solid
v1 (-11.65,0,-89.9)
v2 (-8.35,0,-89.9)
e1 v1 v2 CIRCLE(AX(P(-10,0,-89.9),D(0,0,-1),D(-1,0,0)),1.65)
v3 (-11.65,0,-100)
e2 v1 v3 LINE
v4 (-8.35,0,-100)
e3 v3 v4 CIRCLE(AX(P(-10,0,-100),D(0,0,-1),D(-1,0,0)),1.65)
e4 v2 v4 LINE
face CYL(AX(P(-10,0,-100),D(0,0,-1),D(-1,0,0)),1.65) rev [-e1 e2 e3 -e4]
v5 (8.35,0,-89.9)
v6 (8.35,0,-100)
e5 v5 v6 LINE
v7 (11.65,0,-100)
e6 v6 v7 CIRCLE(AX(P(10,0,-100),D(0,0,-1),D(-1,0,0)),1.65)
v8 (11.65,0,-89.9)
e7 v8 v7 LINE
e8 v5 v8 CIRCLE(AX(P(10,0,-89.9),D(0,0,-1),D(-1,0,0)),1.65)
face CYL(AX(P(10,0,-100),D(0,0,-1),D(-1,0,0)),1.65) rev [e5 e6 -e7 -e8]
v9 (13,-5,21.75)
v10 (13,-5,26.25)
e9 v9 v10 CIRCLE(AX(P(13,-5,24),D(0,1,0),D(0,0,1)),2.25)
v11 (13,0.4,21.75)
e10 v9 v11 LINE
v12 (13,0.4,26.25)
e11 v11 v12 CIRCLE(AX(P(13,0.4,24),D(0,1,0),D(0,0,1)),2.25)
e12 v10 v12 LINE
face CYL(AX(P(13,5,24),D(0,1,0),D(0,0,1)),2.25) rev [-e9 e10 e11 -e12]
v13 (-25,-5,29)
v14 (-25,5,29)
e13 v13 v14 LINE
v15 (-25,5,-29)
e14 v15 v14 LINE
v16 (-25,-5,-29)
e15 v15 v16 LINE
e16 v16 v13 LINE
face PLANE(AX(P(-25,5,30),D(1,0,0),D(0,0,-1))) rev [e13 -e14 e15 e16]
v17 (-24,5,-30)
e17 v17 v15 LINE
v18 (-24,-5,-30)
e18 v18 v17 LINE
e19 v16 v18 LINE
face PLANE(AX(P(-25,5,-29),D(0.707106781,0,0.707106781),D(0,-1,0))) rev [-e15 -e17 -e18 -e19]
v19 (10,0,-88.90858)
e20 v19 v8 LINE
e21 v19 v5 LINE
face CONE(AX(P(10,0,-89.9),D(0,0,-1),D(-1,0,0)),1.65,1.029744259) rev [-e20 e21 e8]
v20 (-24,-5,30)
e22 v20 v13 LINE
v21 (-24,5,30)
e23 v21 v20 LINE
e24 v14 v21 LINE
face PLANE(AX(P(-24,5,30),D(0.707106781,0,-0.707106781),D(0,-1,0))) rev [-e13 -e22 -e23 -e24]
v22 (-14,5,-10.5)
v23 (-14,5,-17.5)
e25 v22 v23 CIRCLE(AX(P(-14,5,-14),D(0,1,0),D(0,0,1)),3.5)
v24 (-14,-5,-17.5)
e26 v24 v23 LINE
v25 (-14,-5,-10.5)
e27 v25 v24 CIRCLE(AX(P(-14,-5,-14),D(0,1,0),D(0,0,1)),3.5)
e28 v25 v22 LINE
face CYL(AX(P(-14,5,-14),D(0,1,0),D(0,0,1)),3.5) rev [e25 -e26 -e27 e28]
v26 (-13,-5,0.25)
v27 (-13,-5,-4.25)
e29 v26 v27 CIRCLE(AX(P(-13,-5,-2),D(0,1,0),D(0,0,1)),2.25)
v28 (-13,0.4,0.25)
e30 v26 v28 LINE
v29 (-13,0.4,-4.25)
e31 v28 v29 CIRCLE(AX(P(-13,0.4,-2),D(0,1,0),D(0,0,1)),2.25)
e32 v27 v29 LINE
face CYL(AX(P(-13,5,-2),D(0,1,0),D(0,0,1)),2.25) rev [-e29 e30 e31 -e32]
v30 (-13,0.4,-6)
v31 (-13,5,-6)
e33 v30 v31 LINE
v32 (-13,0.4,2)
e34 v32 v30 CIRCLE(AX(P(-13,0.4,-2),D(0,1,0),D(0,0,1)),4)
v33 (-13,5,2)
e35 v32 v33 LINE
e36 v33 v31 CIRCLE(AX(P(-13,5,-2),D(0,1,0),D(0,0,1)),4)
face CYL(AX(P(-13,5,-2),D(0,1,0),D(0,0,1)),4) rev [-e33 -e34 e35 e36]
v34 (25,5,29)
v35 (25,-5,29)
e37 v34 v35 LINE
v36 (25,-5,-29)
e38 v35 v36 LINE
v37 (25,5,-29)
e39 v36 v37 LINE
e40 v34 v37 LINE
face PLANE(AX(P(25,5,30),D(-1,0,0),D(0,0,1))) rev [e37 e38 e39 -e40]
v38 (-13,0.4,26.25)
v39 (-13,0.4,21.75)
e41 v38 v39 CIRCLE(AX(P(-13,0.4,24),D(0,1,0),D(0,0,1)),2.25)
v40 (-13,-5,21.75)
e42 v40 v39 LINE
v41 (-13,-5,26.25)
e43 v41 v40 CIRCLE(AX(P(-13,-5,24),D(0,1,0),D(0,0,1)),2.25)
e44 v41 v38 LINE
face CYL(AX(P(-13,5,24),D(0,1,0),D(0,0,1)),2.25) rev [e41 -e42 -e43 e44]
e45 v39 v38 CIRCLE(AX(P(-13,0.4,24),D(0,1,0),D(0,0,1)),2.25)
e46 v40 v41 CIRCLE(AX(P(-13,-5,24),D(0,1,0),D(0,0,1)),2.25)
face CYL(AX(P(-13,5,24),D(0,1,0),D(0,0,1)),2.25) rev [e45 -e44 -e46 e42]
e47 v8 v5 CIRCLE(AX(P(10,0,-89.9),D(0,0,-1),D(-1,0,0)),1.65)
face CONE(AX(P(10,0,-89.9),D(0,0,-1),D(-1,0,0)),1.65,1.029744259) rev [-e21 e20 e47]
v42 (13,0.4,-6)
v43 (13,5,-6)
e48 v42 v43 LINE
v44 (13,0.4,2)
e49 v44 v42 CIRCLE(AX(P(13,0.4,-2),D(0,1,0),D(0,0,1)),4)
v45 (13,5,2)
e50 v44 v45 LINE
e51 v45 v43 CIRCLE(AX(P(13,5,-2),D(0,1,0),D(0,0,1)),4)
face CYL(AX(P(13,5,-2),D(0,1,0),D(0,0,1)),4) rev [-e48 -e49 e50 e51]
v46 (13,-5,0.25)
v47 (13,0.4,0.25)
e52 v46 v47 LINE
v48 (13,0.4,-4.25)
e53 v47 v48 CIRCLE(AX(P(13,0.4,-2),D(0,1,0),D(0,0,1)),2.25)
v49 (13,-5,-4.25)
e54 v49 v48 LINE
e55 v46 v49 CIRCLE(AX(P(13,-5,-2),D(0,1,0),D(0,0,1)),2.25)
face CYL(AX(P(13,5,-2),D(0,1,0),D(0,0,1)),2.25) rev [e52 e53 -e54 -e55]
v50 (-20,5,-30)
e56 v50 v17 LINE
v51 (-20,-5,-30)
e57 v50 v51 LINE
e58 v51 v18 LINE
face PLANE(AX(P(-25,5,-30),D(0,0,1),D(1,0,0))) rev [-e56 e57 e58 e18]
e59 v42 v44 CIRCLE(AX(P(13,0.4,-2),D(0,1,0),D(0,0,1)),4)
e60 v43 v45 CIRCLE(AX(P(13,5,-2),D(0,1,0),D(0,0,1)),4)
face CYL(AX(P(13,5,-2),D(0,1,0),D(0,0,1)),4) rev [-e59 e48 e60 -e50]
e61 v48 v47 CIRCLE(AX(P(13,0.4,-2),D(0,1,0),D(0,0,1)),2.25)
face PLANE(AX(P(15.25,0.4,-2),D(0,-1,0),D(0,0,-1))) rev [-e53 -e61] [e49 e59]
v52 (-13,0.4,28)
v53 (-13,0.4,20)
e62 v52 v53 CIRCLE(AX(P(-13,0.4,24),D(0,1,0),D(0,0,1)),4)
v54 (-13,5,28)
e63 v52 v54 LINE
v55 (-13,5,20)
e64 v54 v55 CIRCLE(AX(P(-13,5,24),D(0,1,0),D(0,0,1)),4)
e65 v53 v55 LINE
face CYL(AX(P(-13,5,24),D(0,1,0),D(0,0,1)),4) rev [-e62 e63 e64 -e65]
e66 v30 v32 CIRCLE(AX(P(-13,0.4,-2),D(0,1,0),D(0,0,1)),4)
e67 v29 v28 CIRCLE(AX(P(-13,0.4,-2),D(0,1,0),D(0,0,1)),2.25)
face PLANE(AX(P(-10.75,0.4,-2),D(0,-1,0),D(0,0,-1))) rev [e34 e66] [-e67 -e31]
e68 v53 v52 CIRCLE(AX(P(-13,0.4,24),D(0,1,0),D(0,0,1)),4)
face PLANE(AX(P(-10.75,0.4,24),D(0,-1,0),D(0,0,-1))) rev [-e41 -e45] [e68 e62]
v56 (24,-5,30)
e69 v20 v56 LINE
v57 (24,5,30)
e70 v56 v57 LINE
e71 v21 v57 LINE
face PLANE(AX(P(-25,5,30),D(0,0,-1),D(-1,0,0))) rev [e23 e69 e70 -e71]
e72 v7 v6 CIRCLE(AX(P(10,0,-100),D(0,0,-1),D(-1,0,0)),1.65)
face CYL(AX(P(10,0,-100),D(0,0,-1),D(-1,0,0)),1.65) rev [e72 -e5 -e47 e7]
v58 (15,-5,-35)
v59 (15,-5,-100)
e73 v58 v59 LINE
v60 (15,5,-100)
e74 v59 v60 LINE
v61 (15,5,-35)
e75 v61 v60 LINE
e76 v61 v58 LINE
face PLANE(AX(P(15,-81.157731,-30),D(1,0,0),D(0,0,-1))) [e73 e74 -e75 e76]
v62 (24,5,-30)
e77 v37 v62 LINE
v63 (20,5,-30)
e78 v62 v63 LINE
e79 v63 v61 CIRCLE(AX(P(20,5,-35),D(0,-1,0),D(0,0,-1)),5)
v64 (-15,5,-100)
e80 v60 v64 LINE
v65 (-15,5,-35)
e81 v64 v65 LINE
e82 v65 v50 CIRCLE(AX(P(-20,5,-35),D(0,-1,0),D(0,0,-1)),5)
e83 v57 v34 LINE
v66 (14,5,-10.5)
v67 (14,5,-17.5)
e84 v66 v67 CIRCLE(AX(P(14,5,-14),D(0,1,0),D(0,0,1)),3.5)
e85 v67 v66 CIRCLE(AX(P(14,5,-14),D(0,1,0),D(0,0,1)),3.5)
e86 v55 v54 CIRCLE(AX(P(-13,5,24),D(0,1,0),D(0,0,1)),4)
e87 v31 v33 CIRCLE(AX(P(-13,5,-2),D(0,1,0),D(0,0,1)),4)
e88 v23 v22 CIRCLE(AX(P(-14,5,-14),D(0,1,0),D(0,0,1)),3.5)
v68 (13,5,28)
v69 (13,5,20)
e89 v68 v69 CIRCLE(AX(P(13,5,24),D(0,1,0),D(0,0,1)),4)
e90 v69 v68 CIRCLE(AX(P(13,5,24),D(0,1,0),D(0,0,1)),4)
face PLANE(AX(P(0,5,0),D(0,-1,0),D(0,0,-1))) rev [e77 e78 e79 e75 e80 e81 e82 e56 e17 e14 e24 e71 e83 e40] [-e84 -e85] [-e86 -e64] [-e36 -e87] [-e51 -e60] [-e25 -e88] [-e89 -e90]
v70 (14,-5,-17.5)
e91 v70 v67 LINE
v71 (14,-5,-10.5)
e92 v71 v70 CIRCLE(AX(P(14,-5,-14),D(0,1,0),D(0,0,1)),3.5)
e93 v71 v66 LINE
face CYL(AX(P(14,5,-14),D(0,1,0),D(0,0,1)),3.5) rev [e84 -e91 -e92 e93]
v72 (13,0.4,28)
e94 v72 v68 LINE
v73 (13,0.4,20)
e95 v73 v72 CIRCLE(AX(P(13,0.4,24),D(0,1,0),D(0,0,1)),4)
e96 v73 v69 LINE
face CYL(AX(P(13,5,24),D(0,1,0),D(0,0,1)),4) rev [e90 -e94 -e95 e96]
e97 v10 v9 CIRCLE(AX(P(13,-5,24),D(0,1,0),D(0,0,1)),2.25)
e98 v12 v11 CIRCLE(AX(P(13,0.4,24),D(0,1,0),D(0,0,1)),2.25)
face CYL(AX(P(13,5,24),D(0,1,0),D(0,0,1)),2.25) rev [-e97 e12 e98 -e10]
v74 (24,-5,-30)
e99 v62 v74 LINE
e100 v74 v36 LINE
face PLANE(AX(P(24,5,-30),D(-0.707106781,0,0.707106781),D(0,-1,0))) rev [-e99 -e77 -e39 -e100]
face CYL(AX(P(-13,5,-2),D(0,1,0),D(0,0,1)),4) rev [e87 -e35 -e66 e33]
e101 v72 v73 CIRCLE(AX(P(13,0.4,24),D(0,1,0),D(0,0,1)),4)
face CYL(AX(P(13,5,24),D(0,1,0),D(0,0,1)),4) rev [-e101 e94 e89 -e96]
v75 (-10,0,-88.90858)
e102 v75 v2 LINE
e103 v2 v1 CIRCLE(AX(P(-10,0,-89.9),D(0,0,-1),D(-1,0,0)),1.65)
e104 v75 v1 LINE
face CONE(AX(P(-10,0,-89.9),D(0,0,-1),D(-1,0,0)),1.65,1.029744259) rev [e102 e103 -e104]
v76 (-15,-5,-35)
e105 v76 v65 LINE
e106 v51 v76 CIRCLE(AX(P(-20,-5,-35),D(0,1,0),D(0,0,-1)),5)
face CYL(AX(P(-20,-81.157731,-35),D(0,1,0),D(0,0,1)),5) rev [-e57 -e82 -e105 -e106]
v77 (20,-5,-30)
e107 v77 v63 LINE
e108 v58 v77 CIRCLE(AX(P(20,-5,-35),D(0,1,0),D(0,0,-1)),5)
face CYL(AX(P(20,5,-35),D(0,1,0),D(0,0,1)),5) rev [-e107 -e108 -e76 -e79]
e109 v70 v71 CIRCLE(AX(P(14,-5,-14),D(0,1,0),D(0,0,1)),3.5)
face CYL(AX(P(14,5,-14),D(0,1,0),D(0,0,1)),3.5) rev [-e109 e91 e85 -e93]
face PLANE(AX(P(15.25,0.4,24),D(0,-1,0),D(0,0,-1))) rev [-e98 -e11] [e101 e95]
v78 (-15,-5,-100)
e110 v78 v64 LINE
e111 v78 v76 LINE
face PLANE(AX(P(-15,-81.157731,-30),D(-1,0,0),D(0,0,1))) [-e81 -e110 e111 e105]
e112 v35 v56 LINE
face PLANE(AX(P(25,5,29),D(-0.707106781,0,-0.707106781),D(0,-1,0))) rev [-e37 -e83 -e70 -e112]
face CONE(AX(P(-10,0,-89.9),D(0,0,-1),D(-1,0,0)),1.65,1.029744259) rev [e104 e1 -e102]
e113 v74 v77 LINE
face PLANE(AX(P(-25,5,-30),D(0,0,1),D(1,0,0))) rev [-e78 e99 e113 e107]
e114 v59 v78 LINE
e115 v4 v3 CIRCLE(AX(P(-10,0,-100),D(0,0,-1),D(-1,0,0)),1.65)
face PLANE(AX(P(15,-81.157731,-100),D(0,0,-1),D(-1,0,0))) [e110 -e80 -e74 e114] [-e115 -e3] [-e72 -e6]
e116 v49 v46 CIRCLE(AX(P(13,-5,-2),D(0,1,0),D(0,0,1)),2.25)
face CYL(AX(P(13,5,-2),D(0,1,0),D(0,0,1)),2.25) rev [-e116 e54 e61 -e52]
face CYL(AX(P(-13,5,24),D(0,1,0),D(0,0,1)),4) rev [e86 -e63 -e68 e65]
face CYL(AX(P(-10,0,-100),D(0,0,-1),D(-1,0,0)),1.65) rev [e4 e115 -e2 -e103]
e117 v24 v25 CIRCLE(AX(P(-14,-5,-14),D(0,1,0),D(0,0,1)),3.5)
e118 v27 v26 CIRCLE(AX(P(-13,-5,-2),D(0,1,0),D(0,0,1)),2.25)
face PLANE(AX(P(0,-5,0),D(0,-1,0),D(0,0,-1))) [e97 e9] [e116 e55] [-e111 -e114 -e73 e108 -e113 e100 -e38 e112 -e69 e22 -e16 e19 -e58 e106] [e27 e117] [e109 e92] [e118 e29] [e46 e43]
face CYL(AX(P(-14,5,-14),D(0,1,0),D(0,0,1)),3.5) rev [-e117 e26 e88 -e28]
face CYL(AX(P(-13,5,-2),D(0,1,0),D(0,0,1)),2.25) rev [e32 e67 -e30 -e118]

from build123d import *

# Parameters (mm, degrees)
SKETCH_1_W                = 50
SKETCH_1_H                = 60
EXTRUDE_1_DEPTH           = 5
HOLE_WIZARD_1_D           = 4.5
HOLE_WIZARD_1_CBORE_D     = 8
HOLE_WIZARD_1_CBORE_DEPTH = 4.6
M8X1_0_1_D                = 7
SKETCH_8_W                = 30
SKETCH_8_H                = 70
EXTRUDE_2_DEPTH           = 10
CHAMFER_1_SIZE            = 1
FILLET_1_R                = 5
HOLE_WIZARD_M4_1_D        = 3.3
HOLE_WIZARD_M4_1_DEPTH    = 10.1
HOLE_WIZARD_M4_1_TIP      = 0.991420021


with BuildPart() as part:
    # 草图1 → 凸台-拉伸1 (new, symmetric)
    with BuildSketch(Plane(origin=(0, 0, 0), x_dir=(1, 0, 0), z_dir=(0, 1, 0))):
        Rectangle(SKETCH_1_W, SKETCH_1_H)
    extrude(amount=EXTRUDE_1_DEPTH, both=True)

    # 打孔尺寸(%根据)内六角圆柱头螺钉的类型1 (through all)
    with Locations(Plane(origin=(0, 5, 0), x_dir=(1, 0, 0), z_dir=(0, 1, 0))):
        with Locations((13, -24), (13, 2), (-13, 2), (-13, -24)):
            CounterBoreHole(HOLE_WIZARD_1_D / 2, HOLE_WIZARD_1_CBORE_D / 2, HOLE_WIZARD_1_CBORE_DEPTH)

    # M8x1.0 螺纹孔1 (through all)
    with Locations(Plane(origin=(0, 5, 0), x_dir=(1, 0, 0), z_dir=(0, 1, 0))):
        with Locations((-14, 14), (14, 14)):
            Hole(M8X1_0_1_D / 2)

    # 草图8 → 凸台-拉伸2 (add)
    with BuildSketch(Plane(origin=(0, 5, 0), x_dir=(1, 0, 0), z_dir=(0, 1, 0))):
        with Locations((0, 65)):
            Rectangle(SKETCH_8_W, SKETCH_8_H)
    extrude(amount=-EXTRUDE_2_DEPTH)

    # 倒角1
    chamfer_1_edges = [part.edges().sort_by_distance(p)[0] for p in [
        (25, 0, 30),
        (-25, 0, 30),
        (-25, 0, -30),
        (25, 0, -30),
    ]]
    chamfer(chamfer_1_edges, length=CHAMFER_1_SIZE)

    # 圆角1
    fillet_1_edges = [part.edges().sort_by_distance(p)[0] for p in [
        (-15, 0, -30),
        (15, 0, -30),
    ]]
    fillet(fillet_1_edges, radius=FILLET_1_R)

    # M4 螺纹孔1
    with Locations(Plane(origin=(0, 0, -100), x_dir=(-1, 0, 0), z_dir=(0, 0, -1))):
        with Locations((10, 0), (-10, 0)):
            Hole(HOLE_WIZARD_M4_1_D / 2, depth=HOLE_WIZARD_M4_1_DEPTH)
            with Locations((0, 0, -(HOLE_WIZARD_M4_1_DEPTH + HOLE_WIZARD_M4_1_TIP / 2))):  # 118° drill point
                Cone(0, HOLE_WIZARD_M4_1_D / 2, HOLE_WIZARD_M4_1_TIP, mode=Mode.SUBTRACT)


solid = part.part
